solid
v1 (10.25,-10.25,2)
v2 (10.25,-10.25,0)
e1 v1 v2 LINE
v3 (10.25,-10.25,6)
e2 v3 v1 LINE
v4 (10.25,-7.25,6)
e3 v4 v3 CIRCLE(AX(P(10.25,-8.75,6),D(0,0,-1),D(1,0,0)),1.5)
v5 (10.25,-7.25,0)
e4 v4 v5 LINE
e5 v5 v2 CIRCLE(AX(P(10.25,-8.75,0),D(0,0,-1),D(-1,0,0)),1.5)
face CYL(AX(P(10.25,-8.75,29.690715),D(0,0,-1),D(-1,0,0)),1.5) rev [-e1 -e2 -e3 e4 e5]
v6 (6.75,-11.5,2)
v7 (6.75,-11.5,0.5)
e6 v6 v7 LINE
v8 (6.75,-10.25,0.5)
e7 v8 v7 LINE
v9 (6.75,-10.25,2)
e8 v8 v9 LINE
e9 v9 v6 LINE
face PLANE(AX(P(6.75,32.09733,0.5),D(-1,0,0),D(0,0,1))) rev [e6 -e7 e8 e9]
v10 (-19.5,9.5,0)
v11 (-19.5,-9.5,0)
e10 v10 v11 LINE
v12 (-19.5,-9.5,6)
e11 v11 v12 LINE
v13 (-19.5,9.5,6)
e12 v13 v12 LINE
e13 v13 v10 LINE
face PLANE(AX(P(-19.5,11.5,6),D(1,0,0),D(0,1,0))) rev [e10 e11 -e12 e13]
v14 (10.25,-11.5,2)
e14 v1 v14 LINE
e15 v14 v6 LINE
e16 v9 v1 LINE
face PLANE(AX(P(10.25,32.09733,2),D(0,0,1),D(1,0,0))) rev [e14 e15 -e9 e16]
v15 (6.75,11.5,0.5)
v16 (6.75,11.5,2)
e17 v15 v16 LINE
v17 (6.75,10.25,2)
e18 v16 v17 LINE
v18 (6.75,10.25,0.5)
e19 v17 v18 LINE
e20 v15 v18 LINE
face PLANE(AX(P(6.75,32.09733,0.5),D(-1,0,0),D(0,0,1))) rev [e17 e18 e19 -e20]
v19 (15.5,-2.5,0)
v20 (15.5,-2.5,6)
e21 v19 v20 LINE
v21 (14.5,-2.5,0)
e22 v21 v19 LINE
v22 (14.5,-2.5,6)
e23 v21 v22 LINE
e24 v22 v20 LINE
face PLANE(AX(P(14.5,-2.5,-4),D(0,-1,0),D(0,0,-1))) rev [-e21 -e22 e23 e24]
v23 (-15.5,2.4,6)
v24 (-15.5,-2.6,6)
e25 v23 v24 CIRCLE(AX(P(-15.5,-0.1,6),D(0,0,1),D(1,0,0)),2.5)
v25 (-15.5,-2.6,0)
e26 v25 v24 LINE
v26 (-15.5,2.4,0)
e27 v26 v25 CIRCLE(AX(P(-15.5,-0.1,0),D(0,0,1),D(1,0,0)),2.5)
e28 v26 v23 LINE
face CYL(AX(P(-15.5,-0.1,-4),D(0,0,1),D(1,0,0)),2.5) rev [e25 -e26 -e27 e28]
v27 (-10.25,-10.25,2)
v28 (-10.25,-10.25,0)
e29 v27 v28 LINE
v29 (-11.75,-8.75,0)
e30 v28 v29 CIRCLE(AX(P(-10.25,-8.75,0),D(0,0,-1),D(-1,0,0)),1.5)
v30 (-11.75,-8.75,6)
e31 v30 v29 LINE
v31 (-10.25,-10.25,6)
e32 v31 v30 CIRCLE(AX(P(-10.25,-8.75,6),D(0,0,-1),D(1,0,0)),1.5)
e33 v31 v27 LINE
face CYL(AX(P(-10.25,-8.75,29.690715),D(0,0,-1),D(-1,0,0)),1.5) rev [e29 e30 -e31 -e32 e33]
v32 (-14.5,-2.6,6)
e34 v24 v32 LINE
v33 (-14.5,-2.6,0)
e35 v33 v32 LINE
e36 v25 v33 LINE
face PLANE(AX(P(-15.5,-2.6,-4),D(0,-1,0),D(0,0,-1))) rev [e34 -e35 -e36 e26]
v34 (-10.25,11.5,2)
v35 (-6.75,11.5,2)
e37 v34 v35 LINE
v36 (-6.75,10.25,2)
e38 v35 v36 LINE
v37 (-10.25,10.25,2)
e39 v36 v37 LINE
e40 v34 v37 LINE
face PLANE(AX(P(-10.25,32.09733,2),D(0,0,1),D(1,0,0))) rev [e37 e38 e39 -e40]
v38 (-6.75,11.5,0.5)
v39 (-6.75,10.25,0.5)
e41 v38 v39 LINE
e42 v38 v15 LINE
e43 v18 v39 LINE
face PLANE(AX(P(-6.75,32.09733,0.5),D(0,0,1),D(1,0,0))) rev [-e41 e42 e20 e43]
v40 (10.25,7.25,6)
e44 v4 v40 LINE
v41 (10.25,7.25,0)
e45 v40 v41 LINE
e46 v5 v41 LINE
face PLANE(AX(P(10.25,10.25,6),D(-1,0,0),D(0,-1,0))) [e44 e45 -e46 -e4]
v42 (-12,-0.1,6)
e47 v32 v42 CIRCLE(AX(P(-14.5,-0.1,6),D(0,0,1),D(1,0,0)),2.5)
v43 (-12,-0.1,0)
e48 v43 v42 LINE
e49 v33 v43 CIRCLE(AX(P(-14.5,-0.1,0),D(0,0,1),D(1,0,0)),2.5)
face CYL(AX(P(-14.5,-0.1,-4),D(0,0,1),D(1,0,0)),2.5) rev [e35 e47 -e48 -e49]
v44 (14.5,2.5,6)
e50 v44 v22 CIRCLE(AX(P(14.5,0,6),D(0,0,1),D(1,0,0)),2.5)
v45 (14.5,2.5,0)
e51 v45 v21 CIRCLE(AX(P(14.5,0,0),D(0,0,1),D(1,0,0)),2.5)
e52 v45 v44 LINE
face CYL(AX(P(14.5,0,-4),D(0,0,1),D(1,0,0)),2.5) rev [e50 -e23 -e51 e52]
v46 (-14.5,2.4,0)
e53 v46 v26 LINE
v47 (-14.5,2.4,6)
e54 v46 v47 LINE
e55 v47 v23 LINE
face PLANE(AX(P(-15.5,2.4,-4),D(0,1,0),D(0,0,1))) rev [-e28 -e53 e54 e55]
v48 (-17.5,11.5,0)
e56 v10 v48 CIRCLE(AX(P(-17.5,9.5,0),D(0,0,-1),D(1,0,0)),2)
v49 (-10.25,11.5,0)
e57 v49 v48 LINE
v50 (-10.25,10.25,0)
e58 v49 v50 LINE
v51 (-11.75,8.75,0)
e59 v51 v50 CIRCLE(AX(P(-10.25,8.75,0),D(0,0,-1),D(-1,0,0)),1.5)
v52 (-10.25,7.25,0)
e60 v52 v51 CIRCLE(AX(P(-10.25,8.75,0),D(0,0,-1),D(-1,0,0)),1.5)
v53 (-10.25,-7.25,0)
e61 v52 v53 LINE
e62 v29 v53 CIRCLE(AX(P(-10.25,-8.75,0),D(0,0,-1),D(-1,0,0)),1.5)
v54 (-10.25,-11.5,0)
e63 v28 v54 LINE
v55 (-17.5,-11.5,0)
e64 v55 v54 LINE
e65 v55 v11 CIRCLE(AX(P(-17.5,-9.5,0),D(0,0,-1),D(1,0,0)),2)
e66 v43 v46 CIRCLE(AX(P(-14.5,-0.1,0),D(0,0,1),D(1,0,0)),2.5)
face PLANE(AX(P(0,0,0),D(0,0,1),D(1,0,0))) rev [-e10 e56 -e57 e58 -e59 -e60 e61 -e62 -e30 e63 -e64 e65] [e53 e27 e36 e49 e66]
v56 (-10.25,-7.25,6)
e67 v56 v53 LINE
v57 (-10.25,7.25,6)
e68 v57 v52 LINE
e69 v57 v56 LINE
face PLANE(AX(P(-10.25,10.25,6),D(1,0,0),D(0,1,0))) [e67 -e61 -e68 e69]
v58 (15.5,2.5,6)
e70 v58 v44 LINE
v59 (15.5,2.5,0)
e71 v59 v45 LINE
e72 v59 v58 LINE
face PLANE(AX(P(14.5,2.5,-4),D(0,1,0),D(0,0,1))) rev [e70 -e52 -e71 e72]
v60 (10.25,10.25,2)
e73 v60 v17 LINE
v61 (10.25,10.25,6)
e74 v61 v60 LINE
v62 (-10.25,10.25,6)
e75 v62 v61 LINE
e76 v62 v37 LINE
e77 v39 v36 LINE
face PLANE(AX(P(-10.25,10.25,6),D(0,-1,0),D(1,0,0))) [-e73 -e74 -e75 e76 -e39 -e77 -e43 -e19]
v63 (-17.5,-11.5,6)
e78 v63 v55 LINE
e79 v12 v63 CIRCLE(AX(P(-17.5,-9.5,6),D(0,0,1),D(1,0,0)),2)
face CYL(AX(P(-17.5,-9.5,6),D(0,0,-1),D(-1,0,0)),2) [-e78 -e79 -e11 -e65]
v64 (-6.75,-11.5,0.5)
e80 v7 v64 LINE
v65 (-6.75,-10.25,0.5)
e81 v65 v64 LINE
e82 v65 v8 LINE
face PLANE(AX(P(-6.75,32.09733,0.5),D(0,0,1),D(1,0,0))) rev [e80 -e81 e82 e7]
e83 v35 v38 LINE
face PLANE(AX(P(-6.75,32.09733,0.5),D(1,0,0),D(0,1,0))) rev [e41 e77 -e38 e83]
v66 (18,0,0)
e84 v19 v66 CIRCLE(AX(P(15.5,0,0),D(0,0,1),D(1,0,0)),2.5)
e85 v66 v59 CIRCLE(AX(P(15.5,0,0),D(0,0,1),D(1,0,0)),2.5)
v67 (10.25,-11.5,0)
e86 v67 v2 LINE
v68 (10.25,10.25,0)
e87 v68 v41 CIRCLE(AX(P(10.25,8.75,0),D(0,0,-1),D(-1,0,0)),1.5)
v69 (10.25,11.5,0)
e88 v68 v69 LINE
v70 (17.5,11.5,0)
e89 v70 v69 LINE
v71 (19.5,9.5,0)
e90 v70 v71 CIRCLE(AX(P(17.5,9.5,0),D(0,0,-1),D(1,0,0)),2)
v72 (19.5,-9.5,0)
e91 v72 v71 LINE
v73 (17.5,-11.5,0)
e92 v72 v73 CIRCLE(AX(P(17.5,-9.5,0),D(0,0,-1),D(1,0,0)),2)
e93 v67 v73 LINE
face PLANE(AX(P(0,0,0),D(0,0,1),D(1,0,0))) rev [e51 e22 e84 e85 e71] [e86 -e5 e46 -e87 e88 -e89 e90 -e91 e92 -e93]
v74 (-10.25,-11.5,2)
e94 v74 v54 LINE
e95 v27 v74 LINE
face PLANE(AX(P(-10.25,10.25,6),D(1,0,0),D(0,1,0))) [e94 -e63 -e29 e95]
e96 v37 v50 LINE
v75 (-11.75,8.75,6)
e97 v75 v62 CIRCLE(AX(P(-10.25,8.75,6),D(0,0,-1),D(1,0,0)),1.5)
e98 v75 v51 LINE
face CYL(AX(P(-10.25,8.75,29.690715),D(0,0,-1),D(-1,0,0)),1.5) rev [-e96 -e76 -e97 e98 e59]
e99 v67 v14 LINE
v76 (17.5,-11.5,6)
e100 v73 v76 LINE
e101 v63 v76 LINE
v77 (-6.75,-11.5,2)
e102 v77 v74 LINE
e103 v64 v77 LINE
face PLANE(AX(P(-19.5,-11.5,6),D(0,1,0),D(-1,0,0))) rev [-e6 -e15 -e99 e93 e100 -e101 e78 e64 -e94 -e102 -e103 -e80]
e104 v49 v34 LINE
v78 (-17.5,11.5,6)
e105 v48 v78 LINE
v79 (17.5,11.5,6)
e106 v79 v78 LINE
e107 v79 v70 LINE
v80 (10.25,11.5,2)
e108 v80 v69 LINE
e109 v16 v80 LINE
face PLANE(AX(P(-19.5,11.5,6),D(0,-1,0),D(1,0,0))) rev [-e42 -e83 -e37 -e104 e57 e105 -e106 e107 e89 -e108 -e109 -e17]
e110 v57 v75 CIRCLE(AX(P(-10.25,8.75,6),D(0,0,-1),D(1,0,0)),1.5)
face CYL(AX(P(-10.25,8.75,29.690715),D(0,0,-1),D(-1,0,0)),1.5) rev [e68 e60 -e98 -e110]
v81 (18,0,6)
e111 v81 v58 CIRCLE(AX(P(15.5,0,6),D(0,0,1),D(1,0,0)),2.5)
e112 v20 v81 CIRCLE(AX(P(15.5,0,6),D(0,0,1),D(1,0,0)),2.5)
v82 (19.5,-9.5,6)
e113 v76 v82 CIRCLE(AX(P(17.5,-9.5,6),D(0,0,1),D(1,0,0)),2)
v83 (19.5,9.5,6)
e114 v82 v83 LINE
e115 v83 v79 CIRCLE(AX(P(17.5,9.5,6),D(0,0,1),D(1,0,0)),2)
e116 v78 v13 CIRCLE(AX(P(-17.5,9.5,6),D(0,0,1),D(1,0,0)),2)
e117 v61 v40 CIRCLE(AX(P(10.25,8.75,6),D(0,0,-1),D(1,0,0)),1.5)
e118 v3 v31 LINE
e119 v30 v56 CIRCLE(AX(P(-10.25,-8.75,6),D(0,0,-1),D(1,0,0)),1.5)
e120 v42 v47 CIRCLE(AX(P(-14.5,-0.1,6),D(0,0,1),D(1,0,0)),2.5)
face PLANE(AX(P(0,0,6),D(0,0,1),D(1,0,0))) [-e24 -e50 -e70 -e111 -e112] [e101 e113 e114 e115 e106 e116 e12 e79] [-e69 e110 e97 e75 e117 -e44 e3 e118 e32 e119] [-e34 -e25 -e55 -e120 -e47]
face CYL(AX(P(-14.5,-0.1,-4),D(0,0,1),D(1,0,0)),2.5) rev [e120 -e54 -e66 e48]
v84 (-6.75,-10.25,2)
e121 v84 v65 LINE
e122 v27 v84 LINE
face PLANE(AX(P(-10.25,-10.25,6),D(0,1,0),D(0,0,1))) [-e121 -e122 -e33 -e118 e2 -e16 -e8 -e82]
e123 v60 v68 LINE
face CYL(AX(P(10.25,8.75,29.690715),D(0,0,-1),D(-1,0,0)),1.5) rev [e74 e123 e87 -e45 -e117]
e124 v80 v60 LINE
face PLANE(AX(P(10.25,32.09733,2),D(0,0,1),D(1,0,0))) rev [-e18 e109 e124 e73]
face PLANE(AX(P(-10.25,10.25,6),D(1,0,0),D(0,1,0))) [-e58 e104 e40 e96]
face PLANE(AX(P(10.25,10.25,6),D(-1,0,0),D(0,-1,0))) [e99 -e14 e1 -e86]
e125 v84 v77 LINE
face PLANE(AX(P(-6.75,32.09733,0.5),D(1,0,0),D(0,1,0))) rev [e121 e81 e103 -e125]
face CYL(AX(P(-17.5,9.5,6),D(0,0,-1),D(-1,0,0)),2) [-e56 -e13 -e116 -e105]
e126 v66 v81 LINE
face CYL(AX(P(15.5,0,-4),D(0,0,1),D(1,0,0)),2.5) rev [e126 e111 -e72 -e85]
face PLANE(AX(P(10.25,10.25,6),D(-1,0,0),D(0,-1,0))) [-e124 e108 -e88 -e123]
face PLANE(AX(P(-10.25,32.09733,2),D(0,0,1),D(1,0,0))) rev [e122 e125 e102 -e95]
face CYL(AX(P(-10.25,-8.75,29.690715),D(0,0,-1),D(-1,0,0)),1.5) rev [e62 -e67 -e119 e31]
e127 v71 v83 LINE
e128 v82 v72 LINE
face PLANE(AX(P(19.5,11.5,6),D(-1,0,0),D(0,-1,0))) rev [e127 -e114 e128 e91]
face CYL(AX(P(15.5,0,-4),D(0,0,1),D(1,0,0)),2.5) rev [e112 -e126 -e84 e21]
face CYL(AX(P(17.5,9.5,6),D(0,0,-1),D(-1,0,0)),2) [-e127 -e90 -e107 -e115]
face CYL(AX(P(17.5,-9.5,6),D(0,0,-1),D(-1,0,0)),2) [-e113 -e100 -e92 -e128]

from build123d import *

# Parameters (mm, degrees)
SKETCH1_W           = 39
SKETCH1_H           = 23
SKETCH1_W_2         = 20.5
SKETCH1_H_2         = 20.5
BOSS_EXTRUDE1_DEPTH = 6
CUT_EXTRUDE1_REACH  = 32.745
SKETCH2_W           = 20.5
SKETCH2_H           = 4.35
SKETCH3_W           = 20.5
SKETCH3_H           = 1.25
BOSS_EXTRUDE2_DEPTH = 4.35
CUT_EXTRUDE2_REACH  = 32.745
CUT_EXTRUDE3_START  = -6
CUT_EXTRUDE3_DEPTH  = 6
CUT_EXTRUDE4_DEPTH  = 10
FILLET1_R           = 2


with BuildPart() as part:
    # Sketch1 → Boss-Extrude1 (new body)
    with BuildSketch(Plane.XY):
        Rectangle(SKETCH1_W, SKETCH1_H)
        Rectangle(SKETCH1_W_2, SKETCH1_H_2, mode=Mode.SUBTRACT)
    extrude(amount=BOSS_EXTRUDE1_DEPTH)

    # Cut-Extrude1: up to this face of the body (flat: up to its plane)
    cut_extrude1_end = Plane(part.part.faces().sort_by_distance((0, 11.5, 3))[0])
    # Sketch2 → Cut-Extrude1 (cut, up to the picked face)
    with BuildSketch(Plane.XZ.offset(11.5), mode=Mode.PRIVATE) as cut_extrude1_sk1:
        with Locations((0, 3.825)):
            Rectangle(SKETCH2_W, SKETCH2_H)
    cut_extrude1_tool1 = split(extrude(cut_extrude1_sk1.sketch, amount=-CUT_EXTRUDE1_REACH, mode=Mode.PRIVATE), bisect_by=cut_extrude1_end, keep=Keep.BOTH, mode=Mode.PRIVATE)
    add(cut_extrude1_tool1.solids().sort_by(Axis((0, -11.5, 3.825), (0, 1, 0)))[0], mode=Mode.SUBTRACT)

    # Sketch3 → Boss-Extrude2 (add)
    with BuildSketch(Plane.XY.offset(6)):
        with Locations((0, 10.875)):
            Rectangle(SKETCH3_W, SKETCH3_H)
        with Locations((0, -10.875)):
            Rectangle(SKETCH3_W, SKETCH3_H)
    extrude(amount=-BOSS_EXTRUDE2_DEPTH)

    # Cut-Extrude2: up to this face of the body (flat: up to its plane)
    cut_extrude2_end = Plane(part.part.faces().sort_by_distance((0, 11.5, 3))[0])
    # Sketch4 → Cut-Extrude2 (cut, up to the picked face)
    with BuildSketch(Plane.XZ.offset(11.5), mode=Mode.PRIVATE) as cut_extrude2_sk1:
        Polygon((6.75, 0.5), (6.75, 2), (10.25, 2), (10.25, 0), (6.75, 0), (-6.75, 0), (-10.25, 0), (-10.25, 2), (-6.75, 2), (-6.75, 0.5), align=None)
    cut_extrude2_tool1 = split(extrude(cut_extrude2_sk1.sketch, amount=-CUT_EXTRUDE2_REACH, mode=Mode.PRIVATE), bisect_by=cut_extrude2_end, keep=Keep.BOTH, mode=Mode.PRIVATE)
    add(cut_extrude2_tool1.solids().sort_by(Axis((6.955973, -11.5, 1.25), (0, 1, 0)))[0], mode=Mode.SUBTRACT)

    # Sketch5 → Cut-Extrude3 (cut)
    with BuildSketch(Plane(origin=(0, 0, 0), x_dir=(-1, 0, 0), z_dir=(0, 0, -1)).offset(CUT_EXTRUDE3_START)):
        with BuildLine():
            Line((-10.25, 10.25), (10.25, 10.25))
            ThreePointArc((10.25, 10.25), (11.75, 8.75), (10.25, 7.25))
            Line((10.25, 7.25), (-10.25, 7.25))
            ThreePointArc((-10.25, 7.25), (-11.75, 8.75), (-10.25, 10.25))
        make_face()
        with BuildLine():
            Line((-10.25, -7.25), (10.25, -7.25))
            ThreePointArc((10.25, -7.25), (11.75, -8.75), (10.25, -10.25))
            Line((10.25, -10.25), (-10.25, -10.25))
            ThreePointArc((-10.25, -10.25), (-11.75, -8.75), (-10.25, -7.25))
        make_face()
    extrude(amount=CUT_EXTRUDE3_DEPTH, mode=Mode.SUBTRACT)

    # Sketch6 → Cut-Extrude4 (cut)
    with BuildSketch(Plane.XY.offset(6)):
        with BuildLine():
            Line((-15.5, 2.4), (-14.5, 2.4))
            ThreePointArc((-14.5, 2.4), (-12, -0.1), (-14.5, -2.6))
            Line((-14.5, -2.6), (-15.5, -2.6))
            ThreePointArc((-15.5, -2.6), (-18, -0.1), (-15.5, 2.4))
        make_face()
        with BuildLine():
            Line((14.5, 2.5), (15.5, 2.5))
            ThreePointArc((15.5, 2.5), (18, 0), (15.5, -2.5))
            Line((15.5, -2.5), (14.5, -2.5))
            ThreePointArc((14.5, -2.5), (12, 0), (14.5, 2.5))
        make_face()
    extrude(amount=-CUT_EXTRUDE4_DEPTH, mode=Mode.SUBTRACT)

    # Fillet1
    fillet1_edges = [part.edges().sort_by_distance(p)[0] for p in [
        (19.5, -11.5, 3),
        (-19.5, -11.5, 3),
        (-19.5, 11.5, 3),
        (19.5, 11.5, 3),
    ]]
    fillet(fillet1_edges, radius=FILLET1_R)


solid = part.part
